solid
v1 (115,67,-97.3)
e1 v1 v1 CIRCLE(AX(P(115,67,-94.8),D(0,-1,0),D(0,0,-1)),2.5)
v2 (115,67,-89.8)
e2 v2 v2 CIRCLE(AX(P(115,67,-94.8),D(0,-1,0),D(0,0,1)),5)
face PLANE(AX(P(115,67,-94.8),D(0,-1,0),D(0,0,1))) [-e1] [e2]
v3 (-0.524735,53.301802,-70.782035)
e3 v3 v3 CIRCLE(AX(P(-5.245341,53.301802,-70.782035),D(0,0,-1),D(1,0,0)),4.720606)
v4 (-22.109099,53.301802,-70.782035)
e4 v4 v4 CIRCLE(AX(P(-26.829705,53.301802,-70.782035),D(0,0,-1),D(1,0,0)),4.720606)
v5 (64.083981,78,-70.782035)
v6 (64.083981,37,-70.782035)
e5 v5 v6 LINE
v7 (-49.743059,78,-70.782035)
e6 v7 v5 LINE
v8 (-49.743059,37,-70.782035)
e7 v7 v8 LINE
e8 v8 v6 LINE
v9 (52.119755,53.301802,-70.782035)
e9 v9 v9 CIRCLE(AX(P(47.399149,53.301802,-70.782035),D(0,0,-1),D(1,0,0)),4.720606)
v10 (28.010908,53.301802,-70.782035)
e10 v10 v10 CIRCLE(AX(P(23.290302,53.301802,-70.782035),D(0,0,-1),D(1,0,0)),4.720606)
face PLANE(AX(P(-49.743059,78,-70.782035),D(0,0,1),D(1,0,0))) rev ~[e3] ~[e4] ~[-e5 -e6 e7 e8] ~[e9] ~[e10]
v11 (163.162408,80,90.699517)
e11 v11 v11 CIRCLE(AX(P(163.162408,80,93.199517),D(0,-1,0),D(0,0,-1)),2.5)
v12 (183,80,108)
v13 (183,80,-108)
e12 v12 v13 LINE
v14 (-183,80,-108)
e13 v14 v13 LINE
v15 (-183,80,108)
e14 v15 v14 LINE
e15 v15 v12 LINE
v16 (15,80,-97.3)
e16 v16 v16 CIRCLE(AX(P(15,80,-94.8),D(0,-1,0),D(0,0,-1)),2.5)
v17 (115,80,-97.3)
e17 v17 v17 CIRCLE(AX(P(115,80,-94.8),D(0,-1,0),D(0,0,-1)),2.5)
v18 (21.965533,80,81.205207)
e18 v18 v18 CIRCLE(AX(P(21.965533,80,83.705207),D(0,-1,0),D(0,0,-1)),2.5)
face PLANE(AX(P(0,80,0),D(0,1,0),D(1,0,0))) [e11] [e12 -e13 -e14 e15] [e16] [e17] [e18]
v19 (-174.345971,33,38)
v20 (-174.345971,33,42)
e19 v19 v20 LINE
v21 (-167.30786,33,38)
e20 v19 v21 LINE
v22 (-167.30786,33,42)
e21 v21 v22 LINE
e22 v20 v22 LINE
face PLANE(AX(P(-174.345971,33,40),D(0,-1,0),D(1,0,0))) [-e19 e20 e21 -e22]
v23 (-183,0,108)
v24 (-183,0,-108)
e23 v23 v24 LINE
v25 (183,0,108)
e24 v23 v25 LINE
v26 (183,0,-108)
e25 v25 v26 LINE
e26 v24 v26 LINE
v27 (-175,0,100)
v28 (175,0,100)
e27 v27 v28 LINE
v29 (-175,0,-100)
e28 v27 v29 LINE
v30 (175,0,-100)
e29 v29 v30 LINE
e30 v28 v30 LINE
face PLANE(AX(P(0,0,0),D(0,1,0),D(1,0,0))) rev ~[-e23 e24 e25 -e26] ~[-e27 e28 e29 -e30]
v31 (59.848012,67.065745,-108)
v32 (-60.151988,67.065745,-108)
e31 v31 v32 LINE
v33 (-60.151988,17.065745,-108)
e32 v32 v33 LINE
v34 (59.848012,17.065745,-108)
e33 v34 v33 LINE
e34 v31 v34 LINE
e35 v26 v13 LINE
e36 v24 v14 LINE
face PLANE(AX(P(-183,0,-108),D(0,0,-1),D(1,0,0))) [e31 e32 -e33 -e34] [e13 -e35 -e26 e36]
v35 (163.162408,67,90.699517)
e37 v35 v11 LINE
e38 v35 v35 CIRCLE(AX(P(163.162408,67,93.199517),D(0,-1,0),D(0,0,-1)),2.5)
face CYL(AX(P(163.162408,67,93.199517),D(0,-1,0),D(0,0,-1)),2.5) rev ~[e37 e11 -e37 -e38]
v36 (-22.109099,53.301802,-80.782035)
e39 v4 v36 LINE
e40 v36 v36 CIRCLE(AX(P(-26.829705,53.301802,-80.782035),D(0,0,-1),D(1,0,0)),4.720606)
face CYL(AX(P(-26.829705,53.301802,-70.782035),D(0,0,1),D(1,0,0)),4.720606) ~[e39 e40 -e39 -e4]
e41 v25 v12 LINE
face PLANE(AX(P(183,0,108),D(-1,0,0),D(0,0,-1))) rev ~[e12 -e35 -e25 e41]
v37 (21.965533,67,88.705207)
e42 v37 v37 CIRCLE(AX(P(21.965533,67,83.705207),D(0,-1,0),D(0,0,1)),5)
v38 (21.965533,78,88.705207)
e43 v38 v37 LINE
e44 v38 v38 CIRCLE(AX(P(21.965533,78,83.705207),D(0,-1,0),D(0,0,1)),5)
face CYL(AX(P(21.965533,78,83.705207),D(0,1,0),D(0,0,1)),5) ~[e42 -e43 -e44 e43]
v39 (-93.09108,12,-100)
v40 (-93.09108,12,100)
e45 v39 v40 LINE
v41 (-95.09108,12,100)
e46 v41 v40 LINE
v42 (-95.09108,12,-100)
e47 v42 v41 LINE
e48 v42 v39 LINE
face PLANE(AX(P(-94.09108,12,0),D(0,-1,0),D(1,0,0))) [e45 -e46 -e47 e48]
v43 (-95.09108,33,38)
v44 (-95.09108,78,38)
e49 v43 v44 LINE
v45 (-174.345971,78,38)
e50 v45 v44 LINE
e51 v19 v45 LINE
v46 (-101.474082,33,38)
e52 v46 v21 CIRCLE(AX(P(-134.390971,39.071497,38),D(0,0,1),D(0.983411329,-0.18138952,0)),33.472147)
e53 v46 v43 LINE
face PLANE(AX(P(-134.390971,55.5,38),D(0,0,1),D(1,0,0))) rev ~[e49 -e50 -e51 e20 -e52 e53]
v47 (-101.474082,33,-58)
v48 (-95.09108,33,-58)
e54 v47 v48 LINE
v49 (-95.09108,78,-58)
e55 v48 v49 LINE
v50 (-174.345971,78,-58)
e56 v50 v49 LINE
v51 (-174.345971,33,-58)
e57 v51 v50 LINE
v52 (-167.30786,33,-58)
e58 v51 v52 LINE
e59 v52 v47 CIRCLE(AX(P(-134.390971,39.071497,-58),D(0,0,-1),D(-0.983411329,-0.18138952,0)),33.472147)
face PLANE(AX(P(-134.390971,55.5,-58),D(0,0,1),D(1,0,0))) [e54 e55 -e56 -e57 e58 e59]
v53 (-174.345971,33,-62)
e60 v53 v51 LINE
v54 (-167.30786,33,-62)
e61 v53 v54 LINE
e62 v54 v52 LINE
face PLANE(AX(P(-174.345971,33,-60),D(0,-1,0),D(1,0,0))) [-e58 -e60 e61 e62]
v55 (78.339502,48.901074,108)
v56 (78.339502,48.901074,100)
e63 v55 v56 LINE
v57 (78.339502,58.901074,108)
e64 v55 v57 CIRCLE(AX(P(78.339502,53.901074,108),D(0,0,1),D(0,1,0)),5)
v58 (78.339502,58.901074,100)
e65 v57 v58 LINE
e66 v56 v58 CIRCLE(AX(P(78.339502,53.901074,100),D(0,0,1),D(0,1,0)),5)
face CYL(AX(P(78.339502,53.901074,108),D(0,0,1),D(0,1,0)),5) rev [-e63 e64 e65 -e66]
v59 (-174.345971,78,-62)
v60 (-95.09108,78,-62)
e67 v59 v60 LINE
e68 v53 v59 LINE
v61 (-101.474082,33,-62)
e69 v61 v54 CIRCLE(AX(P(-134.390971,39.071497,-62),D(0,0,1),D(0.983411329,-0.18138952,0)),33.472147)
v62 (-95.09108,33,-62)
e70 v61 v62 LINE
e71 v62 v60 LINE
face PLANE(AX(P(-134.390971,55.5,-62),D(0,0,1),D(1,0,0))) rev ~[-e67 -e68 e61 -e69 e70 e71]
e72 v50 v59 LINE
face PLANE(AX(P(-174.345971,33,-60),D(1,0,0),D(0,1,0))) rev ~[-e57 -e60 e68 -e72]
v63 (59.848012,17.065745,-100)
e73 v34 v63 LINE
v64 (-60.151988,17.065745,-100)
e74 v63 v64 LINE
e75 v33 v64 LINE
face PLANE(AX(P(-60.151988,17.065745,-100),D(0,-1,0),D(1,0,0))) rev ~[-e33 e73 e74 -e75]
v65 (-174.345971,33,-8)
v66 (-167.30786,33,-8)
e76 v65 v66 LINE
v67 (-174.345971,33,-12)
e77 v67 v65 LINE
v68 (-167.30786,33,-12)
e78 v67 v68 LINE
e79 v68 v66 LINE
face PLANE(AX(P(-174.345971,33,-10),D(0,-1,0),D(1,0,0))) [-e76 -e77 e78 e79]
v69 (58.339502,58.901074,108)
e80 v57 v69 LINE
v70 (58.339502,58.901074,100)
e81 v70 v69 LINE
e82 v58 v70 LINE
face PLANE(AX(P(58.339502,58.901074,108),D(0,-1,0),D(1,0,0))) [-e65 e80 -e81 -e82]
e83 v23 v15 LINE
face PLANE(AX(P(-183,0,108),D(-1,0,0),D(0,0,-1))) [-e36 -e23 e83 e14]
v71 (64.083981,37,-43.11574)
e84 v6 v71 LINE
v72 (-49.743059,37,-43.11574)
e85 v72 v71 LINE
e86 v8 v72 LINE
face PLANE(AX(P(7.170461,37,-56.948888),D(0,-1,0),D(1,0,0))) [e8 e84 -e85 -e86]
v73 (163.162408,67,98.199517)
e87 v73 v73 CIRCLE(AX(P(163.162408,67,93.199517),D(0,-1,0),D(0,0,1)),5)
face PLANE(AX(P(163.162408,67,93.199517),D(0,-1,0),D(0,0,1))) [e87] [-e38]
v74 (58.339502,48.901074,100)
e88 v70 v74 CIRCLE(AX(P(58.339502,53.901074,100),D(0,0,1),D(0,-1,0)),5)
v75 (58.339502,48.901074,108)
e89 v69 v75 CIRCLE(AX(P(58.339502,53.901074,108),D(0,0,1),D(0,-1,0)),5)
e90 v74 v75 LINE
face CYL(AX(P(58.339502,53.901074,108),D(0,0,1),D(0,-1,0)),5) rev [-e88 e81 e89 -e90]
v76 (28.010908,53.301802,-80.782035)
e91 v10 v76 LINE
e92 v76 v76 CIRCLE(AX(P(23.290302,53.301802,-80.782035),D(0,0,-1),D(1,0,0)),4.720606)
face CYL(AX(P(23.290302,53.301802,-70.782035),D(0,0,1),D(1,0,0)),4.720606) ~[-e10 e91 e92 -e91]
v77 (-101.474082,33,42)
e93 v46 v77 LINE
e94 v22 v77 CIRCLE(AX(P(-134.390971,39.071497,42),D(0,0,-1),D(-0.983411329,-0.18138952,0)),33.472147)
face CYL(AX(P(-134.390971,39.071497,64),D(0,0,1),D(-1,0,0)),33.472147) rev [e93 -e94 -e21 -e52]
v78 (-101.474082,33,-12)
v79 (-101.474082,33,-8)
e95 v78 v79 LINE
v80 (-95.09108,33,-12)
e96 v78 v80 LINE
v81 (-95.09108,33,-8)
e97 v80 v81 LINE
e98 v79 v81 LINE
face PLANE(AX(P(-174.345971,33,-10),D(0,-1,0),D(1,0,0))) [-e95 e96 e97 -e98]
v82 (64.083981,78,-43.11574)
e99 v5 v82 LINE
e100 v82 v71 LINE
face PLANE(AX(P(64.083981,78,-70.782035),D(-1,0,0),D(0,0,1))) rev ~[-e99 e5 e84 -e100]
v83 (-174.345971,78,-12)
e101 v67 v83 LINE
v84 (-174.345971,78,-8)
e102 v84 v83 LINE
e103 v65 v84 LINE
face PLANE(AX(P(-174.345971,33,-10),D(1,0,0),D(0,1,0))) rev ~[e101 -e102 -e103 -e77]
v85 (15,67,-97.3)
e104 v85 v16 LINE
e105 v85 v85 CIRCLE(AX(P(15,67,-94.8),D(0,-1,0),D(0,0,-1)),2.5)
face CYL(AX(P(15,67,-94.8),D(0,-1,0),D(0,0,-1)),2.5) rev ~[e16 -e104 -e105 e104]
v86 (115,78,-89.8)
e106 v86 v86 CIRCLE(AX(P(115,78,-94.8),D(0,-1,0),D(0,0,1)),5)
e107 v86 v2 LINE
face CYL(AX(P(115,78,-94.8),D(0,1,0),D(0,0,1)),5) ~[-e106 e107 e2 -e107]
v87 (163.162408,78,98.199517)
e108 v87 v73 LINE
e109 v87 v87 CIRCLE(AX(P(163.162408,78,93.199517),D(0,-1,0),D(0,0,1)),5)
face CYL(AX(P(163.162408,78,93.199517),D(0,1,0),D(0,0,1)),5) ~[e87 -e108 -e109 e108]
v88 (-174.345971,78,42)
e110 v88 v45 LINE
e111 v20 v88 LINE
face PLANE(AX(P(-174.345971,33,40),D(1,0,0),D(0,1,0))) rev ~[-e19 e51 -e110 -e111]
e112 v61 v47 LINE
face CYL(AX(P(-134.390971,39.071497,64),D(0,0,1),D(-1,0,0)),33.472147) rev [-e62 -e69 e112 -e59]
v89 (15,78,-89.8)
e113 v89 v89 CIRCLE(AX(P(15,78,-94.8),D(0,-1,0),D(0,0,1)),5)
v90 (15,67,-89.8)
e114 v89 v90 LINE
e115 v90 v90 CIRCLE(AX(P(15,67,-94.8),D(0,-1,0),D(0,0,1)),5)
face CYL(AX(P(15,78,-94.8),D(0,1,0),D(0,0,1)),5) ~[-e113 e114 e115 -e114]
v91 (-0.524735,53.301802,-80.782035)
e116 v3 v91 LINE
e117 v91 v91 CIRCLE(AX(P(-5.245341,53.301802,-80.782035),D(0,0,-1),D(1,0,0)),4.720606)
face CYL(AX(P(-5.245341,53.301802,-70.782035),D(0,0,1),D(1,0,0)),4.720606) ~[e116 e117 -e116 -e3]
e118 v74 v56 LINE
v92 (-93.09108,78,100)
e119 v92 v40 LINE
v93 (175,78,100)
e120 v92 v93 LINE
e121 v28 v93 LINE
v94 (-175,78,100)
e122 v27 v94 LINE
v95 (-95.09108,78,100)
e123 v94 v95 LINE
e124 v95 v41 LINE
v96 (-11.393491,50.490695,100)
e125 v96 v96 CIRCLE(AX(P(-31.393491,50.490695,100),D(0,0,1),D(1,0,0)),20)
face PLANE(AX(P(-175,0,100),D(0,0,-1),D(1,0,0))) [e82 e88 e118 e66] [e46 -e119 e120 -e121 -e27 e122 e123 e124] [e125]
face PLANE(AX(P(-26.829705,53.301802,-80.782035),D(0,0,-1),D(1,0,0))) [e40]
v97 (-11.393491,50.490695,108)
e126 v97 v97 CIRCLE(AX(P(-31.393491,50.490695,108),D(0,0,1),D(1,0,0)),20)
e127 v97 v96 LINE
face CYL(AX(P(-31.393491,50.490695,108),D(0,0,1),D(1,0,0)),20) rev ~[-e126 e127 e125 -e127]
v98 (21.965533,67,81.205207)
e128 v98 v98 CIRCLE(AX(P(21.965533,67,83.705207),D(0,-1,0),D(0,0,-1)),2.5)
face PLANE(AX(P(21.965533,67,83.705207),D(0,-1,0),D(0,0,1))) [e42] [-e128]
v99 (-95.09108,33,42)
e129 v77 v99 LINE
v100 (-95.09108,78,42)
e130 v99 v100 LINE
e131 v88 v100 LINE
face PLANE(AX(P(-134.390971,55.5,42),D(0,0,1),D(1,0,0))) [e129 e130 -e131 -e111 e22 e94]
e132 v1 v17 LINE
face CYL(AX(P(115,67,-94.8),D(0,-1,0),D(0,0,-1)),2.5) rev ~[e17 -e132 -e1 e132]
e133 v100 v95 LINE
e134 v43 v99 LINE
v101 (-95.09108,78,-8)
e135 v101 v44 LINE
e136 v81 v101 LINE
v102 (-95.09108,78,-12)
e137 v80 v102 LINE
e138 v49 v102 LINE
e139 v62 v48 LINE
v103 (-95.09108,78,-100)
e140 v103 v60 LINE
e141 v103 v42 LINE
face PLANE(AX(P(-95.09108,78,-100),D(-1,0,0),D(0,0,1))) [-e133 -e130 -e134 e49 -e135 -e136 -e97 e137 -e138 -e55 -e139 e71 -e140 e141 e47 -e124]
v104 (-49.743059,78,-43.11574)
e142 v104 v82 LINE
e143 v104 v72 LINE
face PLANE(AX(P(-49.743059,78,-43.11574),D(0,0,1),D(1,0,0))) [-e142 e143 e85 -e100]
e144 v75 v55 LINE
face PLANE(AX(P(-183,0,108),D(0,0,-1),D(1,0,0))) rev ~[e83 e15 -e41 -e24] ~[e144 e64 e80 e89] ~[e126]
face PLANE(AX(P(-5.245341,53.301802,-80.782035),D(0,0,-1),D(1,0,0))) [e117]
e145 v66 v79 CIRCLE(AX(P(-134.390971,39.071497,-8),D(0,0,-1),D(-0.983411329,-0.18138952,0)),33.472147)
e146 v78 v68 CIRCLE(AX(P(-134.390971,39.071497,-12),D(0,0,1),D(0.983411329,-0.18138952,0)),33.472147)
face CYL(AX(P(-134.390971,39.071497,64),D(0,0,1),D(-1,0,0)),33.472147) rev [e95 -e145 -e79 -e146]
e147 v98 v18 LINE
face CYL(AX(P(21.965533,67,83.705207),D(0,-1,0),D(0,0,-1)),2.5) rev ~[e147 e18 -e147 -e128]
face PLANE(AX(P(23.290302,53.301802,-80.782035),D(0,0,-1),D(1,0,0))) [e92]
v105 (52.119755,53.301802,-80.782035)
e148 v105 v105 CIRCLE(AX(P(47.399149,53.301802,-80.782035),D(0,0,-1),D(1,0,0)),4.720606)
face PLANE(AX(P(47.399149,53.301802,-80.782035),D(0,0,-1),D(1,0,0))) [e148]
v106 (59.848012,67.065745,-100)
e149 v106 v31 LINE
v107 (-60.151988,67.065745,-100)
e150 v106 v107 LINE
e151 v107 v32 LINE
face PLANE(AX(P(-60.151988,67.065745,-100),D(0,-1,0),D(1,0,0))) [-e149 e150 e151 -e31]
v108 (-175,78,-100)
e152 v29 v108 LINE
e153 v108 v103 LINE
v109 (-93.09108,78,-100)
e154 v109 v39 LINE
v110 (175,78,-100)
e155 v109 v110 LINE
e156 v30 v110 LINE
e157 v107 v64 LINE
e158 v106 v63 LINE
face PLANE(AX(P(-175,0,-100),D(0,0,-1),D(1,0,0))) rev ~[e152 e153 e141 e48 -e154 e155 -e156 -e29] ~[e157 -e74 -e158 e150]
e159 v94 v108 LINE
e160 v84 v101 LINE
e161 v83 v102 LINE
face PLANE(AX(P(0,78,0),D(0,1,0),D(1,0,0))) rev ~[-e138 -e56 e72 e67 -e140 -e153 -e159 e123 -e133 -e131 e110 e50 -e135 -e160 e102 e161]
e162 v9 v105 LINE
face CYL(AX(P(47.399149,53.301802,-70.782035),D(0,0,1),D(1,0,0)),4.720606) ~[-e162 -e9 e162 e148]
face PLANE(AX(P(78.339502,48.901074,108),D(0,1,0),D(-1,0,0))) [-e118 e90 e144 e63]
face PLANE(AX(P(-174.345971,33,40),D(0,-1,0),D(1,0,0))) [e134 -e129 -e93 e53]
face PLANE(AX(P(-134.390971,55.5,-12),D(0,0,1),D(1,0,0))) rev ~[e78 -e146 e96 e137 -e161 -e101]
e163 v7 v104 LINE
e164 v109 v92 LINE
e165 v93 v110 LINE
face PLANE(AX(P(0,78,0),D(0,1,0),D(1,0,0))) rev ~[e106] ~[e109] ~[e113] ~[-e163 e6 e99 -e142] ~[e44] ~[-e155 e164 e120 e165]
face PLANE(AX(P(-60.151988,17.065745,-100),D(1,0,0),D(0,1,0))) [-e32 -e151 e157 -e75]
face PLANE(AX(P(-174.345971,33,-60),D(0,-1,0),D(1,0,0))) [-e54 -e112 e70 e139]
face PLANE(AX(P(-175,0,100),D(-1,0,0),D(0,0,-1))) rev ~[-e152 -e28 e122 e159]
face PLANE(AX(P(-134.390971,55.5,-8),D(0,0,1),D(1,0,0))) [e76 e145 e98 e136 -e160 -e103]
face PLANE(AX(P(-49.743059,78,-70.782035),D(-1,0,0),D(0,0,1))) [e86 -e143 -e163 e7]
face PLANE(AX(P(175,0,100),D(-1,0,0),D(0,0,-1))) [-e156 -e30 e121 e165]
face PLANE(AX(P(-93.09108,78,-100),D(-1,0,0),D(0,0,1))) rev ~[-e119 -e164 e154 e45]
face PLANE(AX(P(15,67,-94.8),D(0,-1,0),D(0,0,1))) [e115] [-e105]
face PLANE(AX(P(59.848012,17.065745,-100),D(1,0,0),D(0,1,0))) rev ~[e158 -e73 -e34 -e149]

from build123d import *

# Parameters (mm, degrees)
SKETCH2_W               = 366
SKETCH2_H               = 216
SKETCH2_W_2             = 350
SKETCH2_H_2             = 200
BOSS_EXTRUDE1_DEPTH     = 80
SKETCH4_W               = 350
SKETCH4_H               = 200
BOSS_EXTRUDE2_DEPTH     = 2
CUT_EXTRUDE1_DEPTH      = 61
SKETCH6_W               = 120
SKETCH6_H               = 50
CUT_EXTRUDE2_DEPTH      = 61
SKETCH7_R               = 5
SKETCH7_R_2             = 2.5
BOSS_EXTRUDE6_DEPTH     = 11
SKETCH8_R               = 2.5
CUT_EXTRUDE3_DEPTH      = 223.804847344
SKETCH10_R              = 5
BOSS_EXTRUDE7_DEPTH     = 11
SKETCH9_R               = 5
BOSS_EXTRUDE8_DEPTH     = 11
SKETCH11_R              = 2.5
CUT_EXTRUDE4_DEPTH      = 223.804847344
SKETCH12_W              = 2
SKETCH12_H              = 200
EXTRUDE_THIN1_DEPTH     = 66
SKETCH14_W              = 79.91
SKETCH14_H              = 45
BOSS_EXTRUDE9_DEPTH     = 2
LPATTERN1_COUNT         = 3
LPATTERN1_PITCH         = 50
CUT_EXTRUDE5_DEPTH      = 114
CUT_EXTRUDE5_DEPTH_BACK = 26
SKETCH15_R              = 33.472147388
SKETCH16_R              = 20
CUT_EXTRUDE6_DEPTH      = 114
SKETCH20_W              = 113.827039933
SKETCH20_H              = 27.666294428
BOSS_EXTRUDE12_DEPTH    = 41
SKETCH21_R              = 4.720605869
BOSS_EXTRUDE13_DEPTH    = 10


with BuildPart() as part:
    # Sketch2 → Boss-Extrude1 (new body)
    with BuildSketch(Plane(origin=(0, 0, 0), x_dir=(1, 0, 0), z_dir=(0, 1, 0))):
        Rectangle(SKETCH2_W, SKETCH2_H)
        Rectangle(SKETCH2_W_2, SKETCH2_H_2, mode=Mode.SUBTRACT)
    extrude(amount=BOSS_EXTRUDE1_DEPTH)

    # Sketch4 → Boss-Extrude2 (add)
    with BuildSketch(Plane(origin=(0, 80, 0), x_dir=(1, 0, 0), z_dir=(0, 1, 0))):
        Rectangle(SKETCH4_W, SKETCH4_H)
    extrude(amount=-BOSS_EXTRUDE2_DEPTH)

    # Sketch5 → Cut-Extrude1 (cut, symmetric)
    with BuildSketch(Plane.XY.offset(108)):
        with BuildLine():
            Line((58.33950225, 58.901074255), (78.33950225, 58.901074255))
            ThreePointArc((78.33950225, 58.901074255), (83.33950225, 53.901074255), (78.33950225, 48.901074255))
            Line((78.33950225, 48.901074255), (58.33950225, 48.901074255))
            ThreePointArc((58.33950225, 48.901074255), (53.33950225, 53.901074255), (58.33950225, 58.901074255))
        make_face()
    extrude(amount=CUT_EXTRUDE1_DEPTH, both=True, mode=Mode.SUBTRACT)

    # Sketch6 → Cut-Extrude2 (cut, symmetric)
    with BuildSketch(Plane.XY.offset(-100)):
        with Locations((-0.151988162, 42.065744544)):
            Rectangle(SKETCH6_W, SKETCH6_H)
    extrude(amount=CUT_EXTRUDE2_DEPTH, both=True, mode=Mode.SUBTRACT)

    # Sketch7 → Boss-Extrude6 (add)
    # profile 1 of 2: a face of its own
    with BuildSketch(Plane.XZ.offset(-78)):
        with Locations(Location((115, -94.8, 0), (0, 0, 90))):
            Circle(SKETCH7_R)
        with Locations(Location((115, -94.8, 0), (0, 0, 270))):
            Circle(SKETCH7_R_2, mode=Mode.SUBTRACT)
    # profile 2 of 2: a face of its own
    with BuildSketch(Plane.XZ.offset(-78)):
        with Locations(Location((15, -94.8, 0), (0, 0, 90))):
            Circle(SKETCH7_R)
        with Locations(Location((15, -94.8, 0), (0, 0, 270))):
            Circle(SKETCH7_R_2, mode=Mode.SUBTRACT)
    extrude(amount=BOSS_EXTRUDE6_DEPTH)

    # Sketch8 → Cut-Extrude3 (cut, through all)
    with BuildSketch(Plane.XZ.offset(-67)):
        with Locations(Location((15, -94.8, 0), (0, 0, 270))):
            Circle(SKETCH8_R)
        with Locations(Location((115, -94.8, 0), (0, 0, 270))):
            Circle(SKETCH8_R)
    extrude(amount=-CUT_EXTRUDE3_DEPTH, mode=Mode.SUBTRACT)

    # Sketch10 → Boss-Extrude7 (add)
    with BuildSketch(Plane.XZ.offset(-78)):
        with Locations(Location((163.162408198, 93.199516901, 0), (0, 0, 90))):
            Circle(SKETCH10_R)
    extrude(amount=BOSS_EXTRUDE7_DEPTH)

    # Sketch9 → Boss-Extrude8 (add)
    with BuildSketch(Plane.XZ.offset(-78)):
        with Locations(Location((21.965532886, 83.705206519, 0), (0, 0, 90))):
            Circle(SKETCH9_R)
    extrude(amount=BOSS_EXTRUDE8_DEPTH)

    # Sketch11 → Cut-Extrude4 (cut, through all)
    with BuildSketch(Plane.XZ.offset(-67)):
        with Locations(Location((21.965532886, 83.705206519, 0), (0, 0, 270))):
            Circle(SKETCH11_R)
        with Locations(Location((163.162408198, 93.199516901, 0), (0, 0, 270))):
            Circle(SKETCH11_R)
    extrude(amount=-CUT_EXTRUDE4_DEPTH, mode=Mode.SUBTRACT)

    # Sketch12 → Extrude-Thin1 (add)
    with BuildSketch(Plane.XZ.offset(-78)):
        with Locations((-94.091079546, 0)):
            Rectangle(SKETCH12_W, SKETCH12_H)
    extrude(amount=EXTRUDE_THIN1_DEPTH)

    # Sketch14 → Boss-Extrude9 (add, symmetric)
    with BuildSketch(Plane.XY.offset(40)):
        with Locations((-134.390971406, 55.5)):
            Rectangle(SKETCH14_W, SKETCH14_H)
    boss_extrude9 = extrude(amount=BOSS_EXTRUDE9_DEPTH, both=True)

    # LPattern1: Boss-Extrude9 ×3
    with Locations(*[(0, 0, -i * LPATTERN1_PITCH) for i in range(1, LPATTERN1_COUNT)]):
        add(boss_extrude9)

    # Sketch15 → Cut-Extrude5 (cut, two sides: drawn at the far end of the back side and taken through both)
    with BuildSketch(Plane(origin=(0, 0, 38), x_dir=(-1, 0, 0), z_dir=(0, 0, -1)).offset(-CUT_EXTRUDE5_DEPTH_BACK)):
        with Locations((134.390971406, 39.071496759)):
            Circle(SKETCH15_R)
    extrude(amount=CUT_EXTRUDE5_DEPTH + CUT_EXTRUDE5_DEPTH_BACK, mode=Mode.SUBTRACT)

    # Sketch16 → Cut-Extrude6 (cut)
    with BuildSketch(Plane.XY.offset(108)):
        with Locations((-31.393490916, 50.490695355)):
            Circle(SKETCH16_R)
    extrude(amount=-CUT_EXTRUDE6_DEPTH, mode=Mode.SUBTRACT)

    # Sketch20 → Boss-Extrude12 (add)
    with BuildSketch(Plane.XZ.offset(-78)):
        with Locations((7.170460987, -56.94888764)):
            Rectangle(SKETCH20_W, SKETCH20_H)
    extrude(amount=BOSS_EXTRUDE12_DEPTH)

    # Sketch21 → Boss-Extrude13 (add)
    with BuildSketch(Plane(origin=(0, 0, -70.782034854), x_dir=(-1, 0, 0), z_dir=(0, 0, -1))):
        with Locations(Location((-47.399149027, 53.301801825, 0), (0, 0, 180))):
            Circle(SKETCH21_R)
        with Locations(Location((-23.290302455, 53.301801825, 0), (0, 0, 180))):
            Circle(SKETCH21_R)
        with Locations(Location((5.245340735, 53.301801825, 0), (0, 0, 180))):
            Circle(SKETCH21_R)
        with Locations(Location((26.829705026, 53.301801825, 0), (0, 0, 180))):
            Circle(SKETCH21_R)
    extrude(amount=BOSS_EXTRUDE13_DEPTH)


solid = part.part
